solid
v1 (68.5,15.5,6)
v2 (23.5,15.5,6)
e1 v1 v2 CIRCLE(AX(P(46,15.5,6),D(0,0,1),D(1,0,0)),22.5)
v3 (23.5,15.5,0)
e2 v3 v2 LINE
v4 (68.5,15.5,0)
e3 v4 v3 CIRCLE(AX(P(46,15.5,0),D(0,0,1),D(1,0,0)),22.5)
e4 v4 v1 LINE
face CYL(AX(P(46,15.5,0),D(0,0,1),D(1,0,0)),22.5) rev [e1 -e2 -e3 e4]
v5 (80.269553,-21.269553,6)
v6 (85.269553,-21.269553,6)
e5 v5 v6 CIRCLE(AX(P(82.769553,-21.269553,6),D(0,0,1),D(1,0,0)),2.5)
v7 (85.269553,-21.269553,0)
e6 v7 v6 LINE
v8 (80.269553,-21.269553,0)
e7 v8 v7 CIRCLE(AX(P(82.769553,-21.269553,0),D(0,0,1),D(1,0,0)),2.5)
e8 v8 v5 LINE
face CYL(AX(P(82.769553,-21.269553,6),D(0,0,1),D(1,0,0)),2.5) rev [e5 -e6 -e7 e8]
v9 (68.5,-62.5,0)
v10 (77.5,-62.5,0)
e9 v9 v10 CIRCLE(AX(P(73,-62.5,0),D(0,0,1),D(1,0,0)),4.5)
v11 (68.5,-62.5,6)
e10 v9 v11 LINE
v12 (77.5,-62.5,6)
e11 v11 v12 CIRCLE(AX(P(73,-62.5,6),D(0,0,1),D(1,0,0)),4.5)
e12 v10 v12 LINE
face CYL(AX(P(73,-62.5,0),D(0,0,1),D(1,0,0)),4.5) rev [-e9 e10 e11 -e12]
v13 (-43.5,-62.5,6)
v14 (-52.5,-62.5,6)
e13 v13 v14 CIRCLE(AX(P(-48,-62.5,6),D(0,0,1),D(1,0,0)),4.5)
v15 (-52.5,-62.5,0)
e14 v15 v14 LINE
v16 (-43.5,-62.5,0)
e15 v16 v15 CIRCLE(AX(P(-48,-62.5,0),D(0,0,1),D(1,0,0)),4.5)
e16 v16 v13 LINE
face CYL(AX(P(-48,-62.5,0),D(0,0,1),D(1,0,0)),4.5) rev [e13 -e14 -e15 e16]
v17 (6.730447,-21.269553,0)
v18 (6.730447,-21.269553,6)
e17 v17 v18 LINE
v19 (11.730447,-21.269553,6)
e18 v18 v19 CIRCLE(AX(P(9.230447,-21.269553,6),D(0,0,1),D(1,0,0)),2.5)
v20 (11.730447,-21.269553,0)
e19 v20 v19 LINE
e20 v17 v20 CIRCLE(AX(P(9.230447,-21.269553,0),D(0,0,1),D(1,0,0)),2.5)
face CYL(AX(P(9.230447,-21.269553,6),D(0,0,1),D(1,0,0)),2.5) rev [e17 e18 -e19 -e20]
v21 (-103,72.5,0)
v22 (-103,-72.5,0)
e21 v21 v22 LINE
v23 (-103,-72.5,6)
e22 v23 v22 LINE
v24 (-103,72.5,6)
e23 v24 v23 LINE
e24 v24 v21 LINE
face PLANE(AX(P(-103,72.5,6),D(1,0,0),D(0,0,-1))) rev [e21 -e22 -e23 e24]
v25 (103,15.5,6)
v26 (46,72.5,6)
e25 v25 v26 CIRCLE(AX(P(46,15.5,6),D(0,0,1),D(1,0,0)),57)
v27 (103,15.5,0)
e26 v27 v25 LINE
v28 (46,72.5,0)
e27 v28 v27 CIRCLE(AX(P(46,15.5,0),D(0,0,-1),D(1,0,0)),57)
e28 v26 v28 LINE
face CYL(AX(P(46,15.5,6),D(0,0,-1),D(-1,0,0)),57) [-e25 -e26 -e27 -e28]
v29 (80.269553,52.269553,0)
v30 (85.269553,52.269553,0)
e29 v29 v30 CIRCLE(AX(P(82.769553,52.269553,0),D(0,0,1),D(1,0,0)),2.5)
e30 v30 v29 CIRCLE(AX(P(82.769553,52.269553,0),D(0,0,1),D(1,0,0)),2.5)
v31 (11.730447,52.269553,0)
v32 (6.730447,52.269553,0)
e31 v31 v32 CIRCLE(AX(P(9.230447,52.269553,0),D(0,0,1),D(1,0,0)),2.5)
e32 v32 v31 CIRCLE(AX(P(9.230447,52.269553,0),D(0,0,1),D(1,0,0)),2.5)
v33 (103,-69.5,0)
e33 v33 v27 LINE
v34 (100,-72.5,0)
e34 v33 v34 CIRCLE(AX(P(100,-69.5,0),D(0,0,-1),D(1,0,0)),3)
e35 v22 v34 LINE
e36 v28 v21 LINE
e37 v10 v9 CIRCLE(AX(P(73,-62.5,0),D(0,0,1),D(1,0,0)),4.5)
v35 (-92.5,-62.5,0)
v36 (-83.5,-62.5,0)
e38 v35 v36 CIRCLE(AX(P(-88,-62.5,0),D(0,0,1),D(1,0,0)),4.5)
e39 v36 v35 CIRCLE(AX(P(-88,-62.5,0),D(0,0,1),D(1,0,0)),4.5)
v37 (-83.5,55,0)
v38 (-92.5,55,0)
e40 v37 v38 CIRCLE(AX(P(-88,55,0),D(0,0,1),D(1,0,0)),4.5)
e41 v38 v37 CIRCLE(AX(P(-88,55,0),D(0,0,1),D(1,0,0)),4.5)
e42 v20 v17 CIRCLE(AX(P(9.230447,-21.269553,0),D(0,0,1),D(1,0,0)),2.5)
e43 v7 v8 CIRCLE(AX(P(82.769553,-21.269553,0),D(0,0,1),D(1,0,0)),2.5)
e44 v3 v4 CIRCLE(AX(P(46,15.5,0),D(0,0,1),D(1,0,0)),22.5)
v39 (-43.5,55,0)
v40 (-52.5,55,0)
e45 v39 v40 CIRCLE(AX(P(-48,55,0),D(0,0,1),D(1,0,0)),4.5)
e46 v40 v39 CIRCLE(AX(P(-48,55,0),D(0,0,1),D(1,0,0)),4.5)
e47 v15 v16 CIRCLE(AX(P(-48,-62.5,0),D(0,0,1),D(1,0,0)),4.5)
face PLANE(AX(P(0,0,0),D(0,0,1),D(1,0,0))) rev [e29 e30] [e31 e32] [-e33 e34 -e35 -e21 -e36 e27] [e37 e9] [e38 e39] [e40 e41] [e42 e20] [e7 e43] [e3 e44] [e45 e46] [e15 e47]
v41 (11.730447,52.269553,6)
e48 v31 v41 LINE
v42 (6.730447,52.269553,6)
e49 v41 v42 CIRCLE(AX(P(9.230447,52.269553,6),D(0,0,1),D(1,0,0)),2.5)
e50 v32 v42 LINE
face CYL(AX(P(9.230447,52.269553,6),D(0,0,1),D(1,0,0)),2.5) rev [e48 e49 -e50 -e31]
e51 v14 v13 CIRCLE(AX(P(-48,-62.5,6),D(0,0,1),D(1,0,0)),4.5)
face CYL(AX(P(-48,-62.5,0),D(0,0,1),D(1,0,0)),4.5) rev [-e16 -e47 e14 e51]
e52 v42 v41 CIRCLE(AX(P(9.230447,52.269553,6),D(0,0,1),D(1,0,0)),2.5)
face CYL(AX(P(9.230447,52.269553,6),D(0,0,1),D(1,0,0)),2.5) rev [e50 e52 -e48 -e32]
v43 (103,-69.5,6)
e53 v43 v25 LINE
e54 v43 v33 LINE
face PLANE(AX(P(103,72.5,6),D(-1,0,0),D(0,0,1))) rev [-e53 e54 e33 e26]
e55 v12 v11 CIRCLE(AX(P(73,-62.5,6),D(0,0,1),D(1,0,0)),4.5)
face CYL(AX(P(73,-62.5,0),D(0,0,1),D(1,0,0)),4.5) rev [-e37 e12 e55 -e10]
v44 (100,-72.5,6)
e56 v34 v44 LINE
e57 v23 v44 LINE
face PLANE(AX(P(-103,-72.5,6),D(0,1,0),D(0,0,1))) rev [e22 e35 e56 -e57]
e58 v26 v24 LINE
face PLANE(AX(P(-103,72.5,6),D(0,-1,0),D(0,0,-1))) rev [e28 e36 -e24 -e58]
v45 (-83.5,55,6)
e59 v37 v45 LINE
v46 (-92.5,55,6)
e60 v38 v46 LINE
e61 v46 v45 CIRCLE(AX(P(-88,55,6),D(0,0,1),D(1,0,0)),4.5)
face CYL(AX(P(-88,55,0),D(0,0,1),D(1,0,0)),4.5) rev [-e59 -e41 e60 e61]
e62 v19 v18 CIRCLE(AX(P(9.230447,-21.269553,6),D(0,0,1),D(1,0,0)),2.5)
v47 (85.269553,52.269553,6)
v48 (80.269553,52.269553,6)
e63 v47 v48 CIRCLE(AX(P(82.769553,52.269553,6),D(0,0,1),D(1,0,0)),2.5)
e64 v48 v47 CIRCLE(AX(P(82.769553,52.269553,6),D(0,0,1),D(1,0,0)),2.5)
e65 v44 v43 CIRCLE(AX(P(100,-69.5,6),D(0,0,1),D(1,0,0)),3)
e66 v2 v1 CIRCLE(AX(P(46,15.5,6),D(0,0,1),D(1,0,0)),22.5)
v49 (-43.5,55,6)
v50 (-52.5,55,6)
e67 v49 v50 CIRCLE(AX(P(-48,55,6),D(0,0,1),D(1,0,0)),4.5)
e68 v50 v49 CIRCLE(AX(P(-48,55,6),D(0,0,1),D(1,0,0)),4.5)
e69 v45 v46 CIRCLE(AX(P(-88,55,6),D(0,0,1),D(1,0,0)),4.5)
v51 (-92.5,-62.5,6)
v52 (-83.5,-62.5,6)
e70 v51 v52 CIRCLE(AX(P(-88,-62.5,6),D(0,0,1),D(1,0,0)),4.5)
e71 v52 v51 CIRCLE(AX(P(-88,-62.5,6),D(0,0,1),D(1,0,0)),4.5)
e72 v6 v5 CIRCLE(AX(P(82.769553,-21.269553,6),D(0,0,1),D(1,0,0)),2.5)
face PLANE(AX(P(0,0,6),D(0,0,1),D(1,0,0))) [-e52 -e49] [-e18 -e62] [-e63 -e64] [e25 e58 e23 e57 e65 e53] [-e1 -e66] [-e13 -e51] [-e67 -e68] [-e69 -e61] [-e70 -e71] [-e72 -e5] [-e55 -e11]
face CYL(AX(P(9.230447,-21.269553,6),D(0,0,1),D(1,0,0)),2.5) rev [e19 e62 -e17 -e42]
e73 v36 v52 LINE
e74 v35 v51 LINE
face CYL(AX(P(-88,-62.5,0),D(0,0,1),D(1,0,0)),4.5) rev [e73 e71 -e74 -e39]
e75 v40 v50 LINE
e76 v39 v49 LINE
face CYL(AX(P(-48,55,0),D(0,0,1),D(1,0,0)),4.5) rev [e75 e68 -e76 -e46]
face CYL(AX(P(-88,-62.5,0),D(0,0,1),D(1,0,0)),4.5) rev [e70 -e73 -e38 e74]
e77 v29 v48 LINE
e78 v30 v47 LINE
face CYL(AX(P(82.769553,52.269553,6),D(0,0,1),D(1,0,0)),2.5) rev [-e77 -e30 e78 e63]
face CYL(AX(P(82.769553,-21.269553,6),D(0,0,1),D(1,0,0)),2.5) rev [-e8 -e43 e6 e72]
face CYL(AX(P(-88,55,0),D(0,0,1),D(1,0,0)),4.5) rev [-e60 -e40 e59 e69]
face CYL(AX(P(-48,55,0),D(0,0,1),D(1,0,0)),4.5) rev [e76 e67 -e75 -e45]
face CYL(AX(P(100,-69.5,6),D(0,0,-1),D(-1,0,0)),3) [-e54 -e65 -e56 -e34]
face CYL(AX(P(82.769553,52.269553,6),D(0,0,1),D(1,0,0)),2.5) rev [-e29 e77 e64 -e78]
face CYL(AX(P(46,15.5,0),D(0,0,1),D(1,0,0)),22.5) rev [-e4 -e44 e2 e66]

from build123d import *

# Parameters (mm, degrees)
SKETCH_1_W               = 206
SKETCH_1_H               = 145
EXTRUDE_1_DEPTH          = 6
SKETCH_3_R               = 4.5
CUT_EXTRUDE_2_DEPTH      = 127.100158604
SKETCH_4_R               = 22.5
CUT_EXTRUDE_3_DEPTH      = 127.100158604
FILLET_1_R               = 57
HOLE_WIZARD_M6_1_D       = 5
PATTERN_CIRCULAR_1_COUNT = 4
SKETCH_11_R              = 4.5
CUT_EXTRUDE_6_DEPTH      = 127.100158604
FILLET_5_R               = 3


with BuildPart() as part:
    # 草图1 → 凸台-拉伸1 (new body)
    with BuildSketch(Plane.XY):
        Rectangle(SKETCH_1_W, SKETCH_1_H)
    extrude(amount=EXTRUDE_1_DEPTH)

    # 草图3 → 切除-拉伸2 (cut, through all)
    with BuildSketch(Plane.XY.offset(6)):
        with Locations((-88, 55)):
            Circle(SKETCH_3_R)
        with Locations((-48, 55)):
            Circle(SKETCH_3_R)
        with Locations((-88, -62.5)):
            Circle(SKETCH_3_R)
        with Locations((-48, -62.5)):
            Circle(SKETCH_3_R)
    extrude(amount=-CUT_EXTRUDE_2_DEPTH, mode=Mode.SUBTRACT)

    # 草图4 → 切除-拉伸3 (cut, through all)
    with BuildSketch(Plane.XY.offset(6)):
        with Locations((46, 15.5)):
            Circle(SKETCH_4_R)
    extrude(amount=-CUT_EXTRUDE_3_DEPTH, mode=Mode.SUBTRACT)

    # 圆角1
    fillet_1_edges = [part.edges().sort_by_distance(p)[0] for p in [
        (103, 72.5, 3),
    ]]
    fillet(fillet_1_edges, radius=FILLET_1_R)

    # M6 螺纹孔1 (through all)
    with Locations(Plane.XY.offset(6)):
        with Locations((9.230447378, 52.269552622)):
            hole_wizard_m6_1 = Hole(HOLE_WIZARD_M6_1_D / 2)

    # 阵列(圆周)1: M6 螺纹孔1 ×4 about axis
    pattern_circular_1_axis = Axis((46, 15.5, 0), (0, 0, 1))
    for i in range(1, PATTERN_CIRCULAR_1_COUNT):
        add(hole_wizard_m6_1.rotate(pattern_circular_1_axis, i * 360 / PATTERN_CIRCULAR_1_COUNT), mode=Mode.SUBTRACT)

    # 草图11 → 切除-拉伸6 (cut, through all)
    with BuildSketch(Plane.XY.offset(6)):
        with Locations((73, -62.5)):
            Circle(SKETCH_11_R)
    extrude(amount=-CUT_EXTRUDE_6_DEPTH, mode=Mode.SUBTRACT)

    # 圆角5
    fillet_5_edges = [part.edges().sort_by_distance(p)[0] for p in [
        (103, -72.5, 3),
    ]]
    fillet(fillet_5_edges, radius=FILLET_5_R)


solid = part.part
